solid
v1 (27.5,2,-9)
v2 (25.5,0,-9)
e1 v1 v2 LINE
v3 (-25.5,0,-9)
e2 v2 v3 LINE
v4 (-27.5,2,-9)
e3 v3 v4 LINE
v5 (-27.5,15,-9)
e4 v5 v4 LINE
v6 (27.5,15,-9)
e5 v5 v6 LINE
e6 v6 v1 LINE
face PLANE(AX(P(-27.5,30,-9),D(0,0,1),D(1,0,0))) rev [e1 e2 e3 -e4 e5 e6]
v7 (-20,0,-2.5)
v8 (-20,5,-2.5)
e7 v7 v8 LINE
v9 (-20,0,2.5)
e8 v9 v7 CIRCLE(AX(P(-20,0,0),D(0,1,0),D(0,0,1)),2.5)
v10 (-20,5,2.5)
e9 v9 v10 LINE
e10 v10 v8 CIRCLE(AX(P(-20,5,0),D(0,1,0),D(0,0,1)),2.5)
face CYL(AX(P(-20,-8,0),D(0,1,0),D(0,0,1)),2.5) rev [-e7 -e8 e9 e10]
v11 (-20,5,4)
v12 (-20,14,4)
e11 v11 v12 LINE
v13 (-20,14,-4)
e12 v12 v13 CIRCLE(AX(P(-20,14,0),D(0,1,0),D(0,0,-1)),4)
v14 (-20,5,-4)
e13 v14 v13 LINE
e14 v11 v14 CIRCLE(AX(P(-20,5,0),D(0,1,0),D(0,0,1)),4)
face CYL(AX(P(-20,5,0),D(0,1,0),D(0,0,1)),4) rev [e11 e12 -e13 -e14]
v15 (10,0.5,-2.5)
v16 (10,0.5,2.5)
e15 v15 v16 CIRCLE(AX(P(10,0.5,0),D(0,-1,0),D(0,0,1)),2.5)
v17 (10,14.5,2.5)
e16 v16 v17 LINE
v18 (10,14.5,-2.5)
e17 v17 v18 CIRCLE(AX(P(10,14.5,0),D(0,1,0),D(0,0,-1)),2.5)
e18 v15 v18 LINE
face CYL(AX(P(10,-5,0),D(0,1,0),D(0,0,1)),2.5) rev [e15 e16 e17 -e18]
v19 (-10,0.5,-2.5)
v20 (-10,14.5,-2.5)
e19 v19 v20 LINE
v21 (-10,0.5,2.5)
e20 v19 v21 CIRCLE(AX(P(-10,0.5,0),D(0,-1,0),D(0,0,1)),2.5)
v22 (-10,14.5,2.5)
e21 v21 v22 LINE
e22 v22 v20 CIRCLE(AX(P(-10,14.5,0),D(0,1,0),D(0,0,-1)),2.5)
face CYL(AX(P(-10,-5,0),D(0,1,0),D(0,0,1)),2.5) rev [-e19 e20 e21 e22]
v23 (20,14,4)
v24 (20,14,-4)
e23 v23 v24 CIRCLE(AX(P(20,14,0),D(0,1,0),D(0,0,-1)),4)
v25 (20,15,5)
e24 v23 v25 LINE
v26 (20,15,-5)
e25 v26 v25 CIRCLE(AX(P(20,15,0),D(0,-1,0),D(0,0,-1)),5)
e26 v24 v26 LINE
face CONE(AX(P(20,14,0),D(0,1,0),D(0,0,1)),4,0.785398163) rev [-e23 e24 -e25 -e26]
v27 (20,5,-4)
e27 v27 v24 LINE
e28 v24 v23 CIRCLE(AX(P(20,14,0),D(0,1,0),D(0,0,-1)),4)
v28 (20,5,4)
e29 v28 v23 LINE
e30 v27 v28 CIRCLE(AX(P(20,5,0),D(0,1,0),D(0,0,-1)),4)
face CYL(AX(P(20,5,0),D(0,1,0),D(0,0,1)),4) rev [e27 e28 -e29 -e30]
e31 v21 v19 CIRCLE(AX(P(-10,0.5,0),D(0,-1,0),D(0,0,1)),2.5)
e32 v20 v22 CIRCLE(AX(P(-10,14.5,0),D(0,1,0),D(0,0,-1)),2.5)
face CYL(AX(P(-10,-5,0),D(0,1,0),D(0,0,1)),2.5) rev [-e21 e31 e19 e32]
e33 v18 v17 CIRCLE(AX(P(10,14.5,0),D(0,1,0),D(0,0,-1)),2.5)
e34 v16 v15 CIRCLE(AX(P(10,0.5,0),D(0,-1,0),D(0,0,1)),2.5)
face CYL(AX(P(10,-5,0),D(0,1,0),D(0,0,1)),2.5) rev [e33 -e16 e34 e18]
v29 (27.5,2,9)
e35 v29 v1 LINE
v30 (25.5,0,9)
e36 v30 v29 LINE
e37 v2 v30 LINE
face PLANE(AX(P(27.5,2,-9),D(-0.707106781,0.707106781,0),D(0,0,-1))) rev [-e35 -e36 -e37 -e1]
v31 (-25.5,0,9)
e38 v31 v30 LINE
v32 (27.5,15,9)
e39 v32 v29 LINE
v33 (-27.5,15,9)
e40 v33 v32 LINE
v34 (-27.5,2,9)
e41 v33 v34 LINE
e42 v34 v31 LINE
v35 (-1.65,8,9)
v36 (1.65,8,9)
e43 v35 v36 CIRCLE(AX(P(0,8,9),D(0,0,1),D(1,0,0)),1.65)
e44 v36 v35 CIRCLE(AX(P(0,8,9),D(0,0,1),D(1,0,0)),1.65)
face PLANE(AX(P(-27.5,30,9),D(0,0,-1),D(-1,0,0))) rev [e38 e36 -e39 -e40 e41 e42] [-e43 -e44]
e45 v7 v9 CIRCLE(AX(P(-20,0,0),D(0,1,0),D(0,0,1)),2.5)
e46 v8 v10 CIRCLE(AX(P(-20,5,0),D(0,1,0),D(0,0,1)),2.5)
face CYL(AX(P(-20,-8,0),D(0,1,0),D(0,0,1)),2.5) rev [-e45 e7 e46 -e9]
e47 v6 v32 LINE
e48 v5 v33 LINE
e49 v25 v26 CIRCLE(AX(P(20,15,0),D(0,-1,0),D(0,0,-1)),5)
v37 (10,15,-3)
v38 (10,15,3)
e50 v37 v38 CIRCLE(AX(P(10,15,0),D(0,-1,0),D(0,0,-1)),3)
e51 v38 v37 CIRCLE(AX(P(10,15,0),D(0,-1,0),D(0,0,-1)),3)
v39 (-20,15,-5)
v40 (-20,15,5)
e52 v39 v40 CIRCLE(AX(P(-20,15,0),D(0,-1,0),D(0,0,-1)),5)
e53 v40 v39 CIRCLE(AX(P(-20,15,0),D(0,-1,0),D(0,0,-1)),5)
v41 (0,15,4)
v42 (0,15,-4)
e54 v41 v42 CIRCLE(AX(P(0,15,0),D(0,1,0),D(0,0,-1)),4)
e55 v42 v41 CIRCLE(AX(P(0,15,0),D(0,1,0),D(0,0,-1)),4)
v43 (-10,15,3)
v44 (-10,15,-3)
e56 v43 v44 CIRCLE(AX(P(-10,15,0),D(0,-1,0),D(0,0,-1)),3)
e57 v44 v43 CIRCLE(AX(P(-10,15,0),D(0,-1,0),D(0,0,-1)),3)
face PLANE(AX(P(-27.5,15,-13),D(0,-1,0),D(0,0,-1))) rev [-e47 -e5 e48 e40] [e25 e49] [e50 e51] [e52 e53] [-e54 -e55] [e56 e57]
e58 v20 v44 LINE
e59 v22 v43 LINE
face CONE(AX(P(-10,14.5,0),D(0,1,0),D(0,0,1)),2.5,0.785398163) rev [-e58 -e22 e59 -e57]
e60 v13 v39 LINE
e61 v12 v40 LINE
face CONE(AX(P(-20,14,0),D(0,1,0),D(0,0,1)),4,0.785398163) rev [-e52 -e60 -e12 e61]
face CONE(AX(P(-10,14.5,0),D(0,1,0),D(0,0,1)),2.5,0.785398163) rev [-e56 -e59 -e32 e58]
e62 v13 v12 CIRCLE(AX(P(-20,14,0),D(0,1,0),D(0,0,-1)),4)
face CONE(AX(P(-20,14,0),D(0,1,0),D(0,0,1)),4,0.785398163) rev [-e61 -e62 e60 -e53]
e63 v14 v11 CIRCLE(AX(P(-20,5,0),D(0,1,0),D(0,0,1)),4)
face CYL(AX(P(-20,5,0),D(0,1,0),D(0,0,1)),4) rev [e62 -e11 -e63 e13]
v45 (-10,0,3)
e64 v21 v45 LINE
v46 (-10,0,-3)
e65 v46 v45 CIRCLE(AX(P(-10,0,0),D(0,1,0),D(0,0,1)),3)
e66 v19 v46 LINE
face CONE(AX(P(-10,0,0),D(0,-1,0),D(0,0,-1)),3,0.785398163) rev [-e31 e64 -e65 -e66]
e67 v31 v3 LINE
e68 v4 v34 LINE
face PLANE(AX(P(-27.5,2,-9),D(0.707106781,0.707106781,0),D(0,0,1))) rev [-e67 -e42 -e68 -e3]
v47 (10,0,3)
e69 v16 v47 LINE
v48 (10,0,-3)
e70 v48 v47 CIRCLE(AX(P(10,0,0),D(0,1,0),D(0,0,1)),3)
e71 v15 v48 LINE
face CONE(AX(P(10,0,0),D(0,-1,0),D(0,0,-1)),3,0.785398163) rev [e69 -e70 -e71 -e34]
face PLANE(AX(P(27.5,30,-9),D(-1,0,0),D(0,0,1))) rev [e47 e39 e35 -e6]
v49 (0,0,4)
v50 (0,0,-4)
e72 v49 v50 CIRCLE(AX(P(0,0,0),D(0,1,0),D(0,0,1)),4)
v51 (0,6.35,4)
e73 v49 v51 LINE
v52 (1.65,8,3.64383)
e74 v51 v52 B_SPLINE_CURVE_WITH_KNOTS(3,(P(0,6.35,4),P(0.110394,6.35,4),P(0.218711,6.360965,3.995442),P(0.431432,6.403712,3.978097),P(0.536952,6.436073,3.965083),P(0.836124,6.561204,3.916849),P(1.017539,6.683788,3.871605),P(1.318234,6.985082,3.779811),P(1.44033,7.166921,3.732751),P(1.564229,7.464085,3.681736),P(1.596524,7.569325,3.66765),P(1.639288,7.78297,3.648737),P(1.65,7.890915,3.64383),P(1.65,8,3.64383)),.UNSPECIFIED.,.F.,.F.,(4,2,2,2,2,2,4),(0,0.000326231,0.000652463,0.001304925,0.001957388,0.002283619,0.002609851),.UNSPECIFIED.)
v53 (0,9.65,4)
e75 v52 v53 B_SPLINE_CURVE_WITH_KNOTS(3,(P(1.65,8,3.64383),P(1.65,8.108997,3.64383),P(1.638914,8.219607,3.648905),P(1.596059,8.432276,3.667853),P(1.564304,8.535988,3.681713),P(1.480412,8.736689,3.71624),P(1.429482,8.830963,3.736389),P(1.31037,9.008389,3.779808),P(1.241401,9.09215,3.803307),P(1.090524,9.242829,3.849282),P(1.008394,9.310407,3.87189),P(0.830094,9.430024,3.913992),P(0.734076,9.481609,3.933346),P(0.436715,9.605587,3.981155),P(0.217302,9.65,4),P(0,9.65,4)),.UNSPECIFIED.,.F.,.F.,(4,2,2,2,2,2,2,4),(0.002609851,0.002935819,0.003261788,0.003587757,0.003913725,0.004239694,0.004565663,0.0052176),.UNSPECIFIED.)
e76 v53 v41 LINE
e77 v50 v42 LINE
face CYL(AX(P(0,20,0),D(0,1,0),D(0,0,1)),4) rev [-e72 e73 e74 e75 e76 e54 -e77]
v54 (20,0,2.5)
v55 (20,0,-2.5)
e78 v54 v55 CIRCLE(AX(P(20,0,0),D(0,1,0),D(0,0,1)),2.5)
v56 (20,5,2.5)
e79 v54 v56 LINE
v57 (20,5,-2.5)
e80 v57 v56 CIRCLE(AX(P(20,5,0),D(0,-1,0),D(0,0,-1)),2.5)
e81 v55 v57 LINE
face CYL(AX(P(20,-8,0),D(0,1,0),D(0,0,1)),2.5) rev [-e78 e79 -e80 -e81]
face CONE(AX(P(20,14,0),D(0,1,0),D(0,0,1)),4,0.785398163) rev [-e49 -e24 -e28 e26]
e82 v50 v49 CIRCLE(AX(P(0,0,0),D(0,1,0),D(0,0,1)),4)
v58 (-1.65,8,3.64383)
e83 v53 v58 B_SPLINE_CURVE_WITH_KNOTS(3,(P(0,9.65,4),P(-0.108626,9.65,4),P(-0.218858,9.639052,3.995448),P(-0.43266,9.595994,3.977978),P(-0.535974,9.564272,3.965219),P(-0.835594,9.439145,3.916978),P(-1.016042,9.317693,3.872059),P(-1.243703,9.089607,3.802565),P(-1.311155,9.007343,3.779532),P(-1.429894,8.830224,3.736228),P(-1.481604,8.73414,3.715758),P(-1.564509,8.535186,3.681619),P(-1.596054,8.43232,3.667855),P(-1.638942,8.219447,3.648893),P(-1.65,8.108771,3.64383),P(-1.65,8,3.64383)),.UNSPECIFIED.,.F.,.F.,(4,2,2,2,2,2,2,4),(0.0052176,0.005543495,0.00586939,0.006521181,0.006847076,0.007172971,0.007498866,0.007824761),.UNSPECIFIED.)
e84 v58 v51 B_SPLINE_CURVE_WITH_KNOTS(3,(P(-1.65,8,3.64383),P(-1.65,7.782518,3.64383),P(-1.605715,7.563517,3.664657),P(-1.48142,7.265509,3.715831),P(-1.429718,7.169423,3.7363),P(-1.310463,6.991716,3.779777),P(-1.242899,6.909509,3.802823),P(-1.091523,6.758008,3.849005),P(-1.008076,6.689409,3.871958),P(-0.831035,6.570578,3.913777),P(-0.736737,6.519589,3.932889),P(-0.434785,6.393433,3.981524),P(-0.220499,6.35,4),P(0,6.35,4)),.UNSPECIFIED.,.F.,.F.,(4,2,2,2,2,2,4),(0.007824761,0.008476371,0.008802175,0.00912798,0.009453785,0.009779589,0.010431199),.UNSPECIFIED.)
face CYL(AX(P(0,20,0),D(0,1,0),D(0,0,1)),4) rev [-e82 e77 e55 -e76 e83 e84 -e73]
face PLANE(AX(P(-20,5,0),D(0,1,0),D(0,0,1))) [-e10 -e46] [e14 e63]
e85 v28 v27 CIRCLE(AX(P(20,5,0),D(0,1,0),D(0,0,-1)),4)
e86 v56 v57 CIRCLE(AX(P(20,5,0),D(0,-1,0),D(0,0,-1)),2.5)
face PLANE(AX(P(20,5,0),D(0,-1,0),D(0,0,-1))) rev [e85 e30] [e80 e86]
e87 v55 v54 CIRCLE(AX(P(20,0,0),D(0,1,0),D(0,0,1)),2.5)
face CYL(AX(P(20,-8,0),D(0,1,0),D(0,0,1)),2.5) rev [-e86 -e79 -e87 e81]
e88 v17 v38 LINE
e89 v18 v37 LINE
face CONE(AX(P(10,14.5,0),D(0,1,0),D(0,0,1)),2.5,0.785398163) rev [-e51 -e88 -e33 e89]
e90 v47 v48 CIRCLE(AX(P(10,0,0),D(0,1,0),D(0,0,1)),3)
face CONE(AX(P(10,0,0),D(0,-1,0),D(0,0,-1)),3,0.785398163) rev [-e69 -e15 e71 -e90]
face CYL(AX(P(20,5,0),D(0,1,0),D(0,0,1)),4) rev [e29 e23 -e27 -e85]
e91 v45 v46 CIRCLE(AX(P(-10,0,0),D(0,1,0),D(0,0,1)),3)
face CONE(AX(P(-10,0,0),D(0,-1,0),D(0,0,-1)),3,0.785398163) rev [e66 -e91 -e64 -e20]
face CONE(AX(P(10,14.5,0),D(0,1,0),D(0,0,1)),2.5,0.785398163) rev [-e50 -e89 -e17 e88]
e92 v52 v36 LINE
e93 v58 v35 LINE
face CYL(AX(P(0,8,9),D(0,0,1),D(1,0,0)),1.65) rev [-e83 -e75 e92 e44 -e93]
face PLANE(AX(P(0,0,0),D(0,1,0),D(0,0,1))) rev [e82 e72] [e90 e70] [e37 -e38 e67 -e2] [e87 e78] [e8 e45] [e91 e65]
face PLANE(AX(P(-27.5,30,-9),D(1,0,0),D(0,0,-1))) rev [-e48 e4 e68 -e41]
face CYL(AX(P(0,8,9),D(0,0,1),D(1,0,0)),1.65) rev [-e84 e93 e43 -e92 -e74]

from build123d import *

# Parameters (mm, degrees)
SKETCH1_W                  = 55
SKETCH1_H                  = 18
BOSS_EXTRUDE1_DEPTH        = 30
SKETCH2_R                  = 4
CUT_EXTRUDE1_DEPTH         = 25
SKETCH3_R                  = 2.5
CUT_EXTRUDE2_DEPTH         = 38
SKETCH4_W                  = 75
SKETCH4_H                  = 27
SKETCH4_R                  = 4
BOSS_EXTRUDE2_DEPTH        = 10
BOSS_EXTRUDE3_START        = 10
SKETCH6_W                  = 75
SKETCH6_H                  = 18
SKETCH6_R                  = 4
BOSS_EXTRUDE3_DEPTH        = 10
SKETCH7_W                  = 75
SKETCH7_H                  = 20
CUT_EXTRUDE3_DEPTH         = 31
SKETCH8_R                  = 1.280962141
CUT_EXTRUDE4_DEPTH         = 24
F_8_2_8_2_DIAMETER_HOLE1_D = 8
CHAMFER1_SIZE              = 2
SKETCH10_R                 = 2.5
CUT_EXTRUDE5_DEPTH         = 25
SKETCH11_R                 = 1.362041629
CUT_EXTRUDE6_DEPTH         = 10
M4_TAPPED_HOLE1_D          = 3.3
M4_TAPPED_HOLE1_DEPTH      = 10.1
M4_TAPPED_HOLE1_TIP        = 0.991420021
SKETCH13_W                 = 55
SKETCH13_H                 = 5
CUT_EXTRUDE7_DEPTH         = 22
CHAMFER2_SIZE              = 0.5
CHAMFER3_SIZE              = 1


with BuildPart() as part:
    # Sketch1 → Boss-Extrude1 (new body)
    with BuildSketch(Plane(origin=(0, 0, 0), x_dir=(1, 0, 0), z_dir=(0, 1, 0))):
        Rectangle(SKETCH1_W, SKETCH1_H)
    extrude(amount=BOSS_EXTRUDE1_DEPTH)

    # Sketch2 → Cut-Extrude1 (cut)
    with BuildSketch(Plane(origin=(0, 30, 0), x_dir=(1, 0, 0), z_dir=(0, 1, 0))):
        with Locations(Location((-20, 0, 0), (0, 0, 270))):
            Circle(SKETCH2_R)
        with Locations(Location((20, 0, 0), (0, 0, 90))):
            Circle(SKETCH2_R)
    extrude(amount=-CUT_EXTRUDE1_DEPTH, mode=Mode.SUBTRACT)

    # Sketch3 → Cut-Extrude2 (cut)
    with BuildSketch(Plane(origin=(0, 30, 0), x_dir=(1, 0, 0), z_dir=(0, 1, 0))):
        with Locations(Location((-20, 0, 0), (0, 0, 270))):
            Circle(SKETCH3_R)
        with Locations(Location((20, 0, 0), (0, 0, 270))):
            Circle(SKETCH3_R)
    extrude(amount=-CUT_EXTRUDE2_DEPTH, mode=Mode.SUBTRACT)

    # Sketch4 → Boss-Extrude2 (add)
    with BuildSketch(Plane(origin=(0, 30, 0), x_dir=(1, 0, 0), z_dir=(0, 1, 0))):
        Rectangle(SKETCH4_W, SKETCH4_H)
        with Locations(Location((-20, 0, 0), (0, 0, 270))):
            Circle(SKETCH4_R, mode=Mode.SUBTRACT)
        with Locations(Location((20, 0, 0), (0, 0, 90))):
            Circle(SKETCH4_R, mode=Mode.SUBTRACT)
    extrude(amount=-BOSS_EXTRUDE2_DEPTH)

    # Sketch6 → Boss-Extrude3 (add)
    with BuildSketch(Plane(origin=(0, 30, 0), x_dir=(1, 0, 0), z_dir=(0, 1, 0)).offset(BOSS_EXTRUDE3_START)):
        Rectangle(SKETCH6_W, SKETCH6_H)
        with Locations(Location((-20, 0, 0), (0, 0, 270))):
            Circle(SKETCH6_R, mode=Mode.SUBTRACT)
        with Locations(Location((20, 0, 0), (0, 0, 270))):
            Circle(SKETCH6_R, mode=Mode.SUBTRACT)
    extrude(amount=-BOSS_EXTRUDE3_DEPTH)

    # Sketch7 → Cut-Extrude3 (cut)
    with BuildSketch(Plane.XY.offset(13.5)):
        with Locations((0, 30)):
            Rectangle(SKETCH7_W, SKETCH7_H)
    extrude(amount=-CUT_EXTRUDE3_DEPTH, mode=Mode.SUBTRACT)

    # Sketch8 → Cut-Extrude4 (cut)
    with BuildSketch(Plane(origin=(0, 20, 0), x_dir=(1, 0, 0), z_dir=(0, 1, 0))):
        with Locations(Location((0, 0, 0), (0, 0, 270))):
            Circle(SKETCH8_R)
    extrude(amount=-CUT_EXTRUDE4_DEPTH, mode=Mode.SUBTRACT)

    # Ø8.2 (8.2) Diameter Hole1 (through all)
    with Locations(Plane.ZX.offset(20)):
        with Locations((0, 0)):
            Hole(F_8_2_8_2_DIAMETER_HOLE1_D / 2)

    # Chamfer1
    chamfer1_edges = [part.edges().sort_by_distance(p)[0] for p in [
        (-27.5, 0, 0),
        (27.5, 0, 0),
    ]]
    chamfer(chamfer1_edges, length=CHAMFER1_SIZE)

    # Sketch10 → Cut-Extrude5 (cut)
    with BuildSketch(Plane(origin=(0, 20, 0), x_dir=(1, 0, 0), z_dir=(0, 1, 0))):
        with Locations(Location((-10, 0, 0), (0, 0, 270))):
            Circle(SKETCH10_R)
        with Locations(Location((10, 0, 0), (0, 0, 270))):
            Circle(SKETCH10_R)
    extrude(amount=-CUT_EXTRUDE5_DEPTH, mode=Mode.SUBTRACT)

    # Sketch11 → Cut-Extrude6 (cut)
    with BuildSketch(Plane.XY.offset(9)):
        with Locations((0, 8)):
            Circle(SKETCH11_R)
    extrude(amount=-CUT_EXTRUDE6_DEPTH, mode=Mode.SUBTRACT)

    # M4 Tapped Hole1
    with Locations(Plane(origin=(0, 8, 9), x_dir=(1, 0, 0), z_dir=(0, 0, 1))):
        with Locations((0, 0)):
            Hole(M4_TAPPED_HOLE1_D / 2, depth=M4_TAPPED_HOLE1_DEPTH)
            with Locations((0, 0, -(M4_TAPPED_HOLE1_DEPTH + M4_TAPPED_HOLE1_TIP / 2))):  # 118° drill point
                Cone(0, M4_TAPPED_HOLE1_D / 2, M4_TAPPED_HOLE1_TIP, mode=Mode.SUBTRACT)

    # Sketch13 → Cut-Extrude7 (cut)
    with BuildSketch(Plane.XY.offset(9)):
        with Locations((0, 17.5)):
            Rectangle(SKETCH13_W, SKETCH13_H)
    extrude(amount=-CUT_EXTRUDE7_DEPTH, mode=Mode.SUBTRACT)

    # Chamfer2
    chamfer2_edges = [part.edges().sort_by_distance(p)[0] for p in [
        (-10, 0, -2.5),
        (10, 0, -2.5),
        (10, 15, -2.5),
        (-10, 15, -2.5),
    ]]
    chamfer(chamfer2_edges, length=CHAMFER2_SIZE)

    # Chamfer3
    chamfer3_edges = [part.edges().sort_by_distance(p)[0] for p in [
        (-20, 15, -4),
        (20, 15, 4),
    ]]
    chamfer(chamfer3_edges, length=CHAMFER3_SIZE)


solid = part.part
